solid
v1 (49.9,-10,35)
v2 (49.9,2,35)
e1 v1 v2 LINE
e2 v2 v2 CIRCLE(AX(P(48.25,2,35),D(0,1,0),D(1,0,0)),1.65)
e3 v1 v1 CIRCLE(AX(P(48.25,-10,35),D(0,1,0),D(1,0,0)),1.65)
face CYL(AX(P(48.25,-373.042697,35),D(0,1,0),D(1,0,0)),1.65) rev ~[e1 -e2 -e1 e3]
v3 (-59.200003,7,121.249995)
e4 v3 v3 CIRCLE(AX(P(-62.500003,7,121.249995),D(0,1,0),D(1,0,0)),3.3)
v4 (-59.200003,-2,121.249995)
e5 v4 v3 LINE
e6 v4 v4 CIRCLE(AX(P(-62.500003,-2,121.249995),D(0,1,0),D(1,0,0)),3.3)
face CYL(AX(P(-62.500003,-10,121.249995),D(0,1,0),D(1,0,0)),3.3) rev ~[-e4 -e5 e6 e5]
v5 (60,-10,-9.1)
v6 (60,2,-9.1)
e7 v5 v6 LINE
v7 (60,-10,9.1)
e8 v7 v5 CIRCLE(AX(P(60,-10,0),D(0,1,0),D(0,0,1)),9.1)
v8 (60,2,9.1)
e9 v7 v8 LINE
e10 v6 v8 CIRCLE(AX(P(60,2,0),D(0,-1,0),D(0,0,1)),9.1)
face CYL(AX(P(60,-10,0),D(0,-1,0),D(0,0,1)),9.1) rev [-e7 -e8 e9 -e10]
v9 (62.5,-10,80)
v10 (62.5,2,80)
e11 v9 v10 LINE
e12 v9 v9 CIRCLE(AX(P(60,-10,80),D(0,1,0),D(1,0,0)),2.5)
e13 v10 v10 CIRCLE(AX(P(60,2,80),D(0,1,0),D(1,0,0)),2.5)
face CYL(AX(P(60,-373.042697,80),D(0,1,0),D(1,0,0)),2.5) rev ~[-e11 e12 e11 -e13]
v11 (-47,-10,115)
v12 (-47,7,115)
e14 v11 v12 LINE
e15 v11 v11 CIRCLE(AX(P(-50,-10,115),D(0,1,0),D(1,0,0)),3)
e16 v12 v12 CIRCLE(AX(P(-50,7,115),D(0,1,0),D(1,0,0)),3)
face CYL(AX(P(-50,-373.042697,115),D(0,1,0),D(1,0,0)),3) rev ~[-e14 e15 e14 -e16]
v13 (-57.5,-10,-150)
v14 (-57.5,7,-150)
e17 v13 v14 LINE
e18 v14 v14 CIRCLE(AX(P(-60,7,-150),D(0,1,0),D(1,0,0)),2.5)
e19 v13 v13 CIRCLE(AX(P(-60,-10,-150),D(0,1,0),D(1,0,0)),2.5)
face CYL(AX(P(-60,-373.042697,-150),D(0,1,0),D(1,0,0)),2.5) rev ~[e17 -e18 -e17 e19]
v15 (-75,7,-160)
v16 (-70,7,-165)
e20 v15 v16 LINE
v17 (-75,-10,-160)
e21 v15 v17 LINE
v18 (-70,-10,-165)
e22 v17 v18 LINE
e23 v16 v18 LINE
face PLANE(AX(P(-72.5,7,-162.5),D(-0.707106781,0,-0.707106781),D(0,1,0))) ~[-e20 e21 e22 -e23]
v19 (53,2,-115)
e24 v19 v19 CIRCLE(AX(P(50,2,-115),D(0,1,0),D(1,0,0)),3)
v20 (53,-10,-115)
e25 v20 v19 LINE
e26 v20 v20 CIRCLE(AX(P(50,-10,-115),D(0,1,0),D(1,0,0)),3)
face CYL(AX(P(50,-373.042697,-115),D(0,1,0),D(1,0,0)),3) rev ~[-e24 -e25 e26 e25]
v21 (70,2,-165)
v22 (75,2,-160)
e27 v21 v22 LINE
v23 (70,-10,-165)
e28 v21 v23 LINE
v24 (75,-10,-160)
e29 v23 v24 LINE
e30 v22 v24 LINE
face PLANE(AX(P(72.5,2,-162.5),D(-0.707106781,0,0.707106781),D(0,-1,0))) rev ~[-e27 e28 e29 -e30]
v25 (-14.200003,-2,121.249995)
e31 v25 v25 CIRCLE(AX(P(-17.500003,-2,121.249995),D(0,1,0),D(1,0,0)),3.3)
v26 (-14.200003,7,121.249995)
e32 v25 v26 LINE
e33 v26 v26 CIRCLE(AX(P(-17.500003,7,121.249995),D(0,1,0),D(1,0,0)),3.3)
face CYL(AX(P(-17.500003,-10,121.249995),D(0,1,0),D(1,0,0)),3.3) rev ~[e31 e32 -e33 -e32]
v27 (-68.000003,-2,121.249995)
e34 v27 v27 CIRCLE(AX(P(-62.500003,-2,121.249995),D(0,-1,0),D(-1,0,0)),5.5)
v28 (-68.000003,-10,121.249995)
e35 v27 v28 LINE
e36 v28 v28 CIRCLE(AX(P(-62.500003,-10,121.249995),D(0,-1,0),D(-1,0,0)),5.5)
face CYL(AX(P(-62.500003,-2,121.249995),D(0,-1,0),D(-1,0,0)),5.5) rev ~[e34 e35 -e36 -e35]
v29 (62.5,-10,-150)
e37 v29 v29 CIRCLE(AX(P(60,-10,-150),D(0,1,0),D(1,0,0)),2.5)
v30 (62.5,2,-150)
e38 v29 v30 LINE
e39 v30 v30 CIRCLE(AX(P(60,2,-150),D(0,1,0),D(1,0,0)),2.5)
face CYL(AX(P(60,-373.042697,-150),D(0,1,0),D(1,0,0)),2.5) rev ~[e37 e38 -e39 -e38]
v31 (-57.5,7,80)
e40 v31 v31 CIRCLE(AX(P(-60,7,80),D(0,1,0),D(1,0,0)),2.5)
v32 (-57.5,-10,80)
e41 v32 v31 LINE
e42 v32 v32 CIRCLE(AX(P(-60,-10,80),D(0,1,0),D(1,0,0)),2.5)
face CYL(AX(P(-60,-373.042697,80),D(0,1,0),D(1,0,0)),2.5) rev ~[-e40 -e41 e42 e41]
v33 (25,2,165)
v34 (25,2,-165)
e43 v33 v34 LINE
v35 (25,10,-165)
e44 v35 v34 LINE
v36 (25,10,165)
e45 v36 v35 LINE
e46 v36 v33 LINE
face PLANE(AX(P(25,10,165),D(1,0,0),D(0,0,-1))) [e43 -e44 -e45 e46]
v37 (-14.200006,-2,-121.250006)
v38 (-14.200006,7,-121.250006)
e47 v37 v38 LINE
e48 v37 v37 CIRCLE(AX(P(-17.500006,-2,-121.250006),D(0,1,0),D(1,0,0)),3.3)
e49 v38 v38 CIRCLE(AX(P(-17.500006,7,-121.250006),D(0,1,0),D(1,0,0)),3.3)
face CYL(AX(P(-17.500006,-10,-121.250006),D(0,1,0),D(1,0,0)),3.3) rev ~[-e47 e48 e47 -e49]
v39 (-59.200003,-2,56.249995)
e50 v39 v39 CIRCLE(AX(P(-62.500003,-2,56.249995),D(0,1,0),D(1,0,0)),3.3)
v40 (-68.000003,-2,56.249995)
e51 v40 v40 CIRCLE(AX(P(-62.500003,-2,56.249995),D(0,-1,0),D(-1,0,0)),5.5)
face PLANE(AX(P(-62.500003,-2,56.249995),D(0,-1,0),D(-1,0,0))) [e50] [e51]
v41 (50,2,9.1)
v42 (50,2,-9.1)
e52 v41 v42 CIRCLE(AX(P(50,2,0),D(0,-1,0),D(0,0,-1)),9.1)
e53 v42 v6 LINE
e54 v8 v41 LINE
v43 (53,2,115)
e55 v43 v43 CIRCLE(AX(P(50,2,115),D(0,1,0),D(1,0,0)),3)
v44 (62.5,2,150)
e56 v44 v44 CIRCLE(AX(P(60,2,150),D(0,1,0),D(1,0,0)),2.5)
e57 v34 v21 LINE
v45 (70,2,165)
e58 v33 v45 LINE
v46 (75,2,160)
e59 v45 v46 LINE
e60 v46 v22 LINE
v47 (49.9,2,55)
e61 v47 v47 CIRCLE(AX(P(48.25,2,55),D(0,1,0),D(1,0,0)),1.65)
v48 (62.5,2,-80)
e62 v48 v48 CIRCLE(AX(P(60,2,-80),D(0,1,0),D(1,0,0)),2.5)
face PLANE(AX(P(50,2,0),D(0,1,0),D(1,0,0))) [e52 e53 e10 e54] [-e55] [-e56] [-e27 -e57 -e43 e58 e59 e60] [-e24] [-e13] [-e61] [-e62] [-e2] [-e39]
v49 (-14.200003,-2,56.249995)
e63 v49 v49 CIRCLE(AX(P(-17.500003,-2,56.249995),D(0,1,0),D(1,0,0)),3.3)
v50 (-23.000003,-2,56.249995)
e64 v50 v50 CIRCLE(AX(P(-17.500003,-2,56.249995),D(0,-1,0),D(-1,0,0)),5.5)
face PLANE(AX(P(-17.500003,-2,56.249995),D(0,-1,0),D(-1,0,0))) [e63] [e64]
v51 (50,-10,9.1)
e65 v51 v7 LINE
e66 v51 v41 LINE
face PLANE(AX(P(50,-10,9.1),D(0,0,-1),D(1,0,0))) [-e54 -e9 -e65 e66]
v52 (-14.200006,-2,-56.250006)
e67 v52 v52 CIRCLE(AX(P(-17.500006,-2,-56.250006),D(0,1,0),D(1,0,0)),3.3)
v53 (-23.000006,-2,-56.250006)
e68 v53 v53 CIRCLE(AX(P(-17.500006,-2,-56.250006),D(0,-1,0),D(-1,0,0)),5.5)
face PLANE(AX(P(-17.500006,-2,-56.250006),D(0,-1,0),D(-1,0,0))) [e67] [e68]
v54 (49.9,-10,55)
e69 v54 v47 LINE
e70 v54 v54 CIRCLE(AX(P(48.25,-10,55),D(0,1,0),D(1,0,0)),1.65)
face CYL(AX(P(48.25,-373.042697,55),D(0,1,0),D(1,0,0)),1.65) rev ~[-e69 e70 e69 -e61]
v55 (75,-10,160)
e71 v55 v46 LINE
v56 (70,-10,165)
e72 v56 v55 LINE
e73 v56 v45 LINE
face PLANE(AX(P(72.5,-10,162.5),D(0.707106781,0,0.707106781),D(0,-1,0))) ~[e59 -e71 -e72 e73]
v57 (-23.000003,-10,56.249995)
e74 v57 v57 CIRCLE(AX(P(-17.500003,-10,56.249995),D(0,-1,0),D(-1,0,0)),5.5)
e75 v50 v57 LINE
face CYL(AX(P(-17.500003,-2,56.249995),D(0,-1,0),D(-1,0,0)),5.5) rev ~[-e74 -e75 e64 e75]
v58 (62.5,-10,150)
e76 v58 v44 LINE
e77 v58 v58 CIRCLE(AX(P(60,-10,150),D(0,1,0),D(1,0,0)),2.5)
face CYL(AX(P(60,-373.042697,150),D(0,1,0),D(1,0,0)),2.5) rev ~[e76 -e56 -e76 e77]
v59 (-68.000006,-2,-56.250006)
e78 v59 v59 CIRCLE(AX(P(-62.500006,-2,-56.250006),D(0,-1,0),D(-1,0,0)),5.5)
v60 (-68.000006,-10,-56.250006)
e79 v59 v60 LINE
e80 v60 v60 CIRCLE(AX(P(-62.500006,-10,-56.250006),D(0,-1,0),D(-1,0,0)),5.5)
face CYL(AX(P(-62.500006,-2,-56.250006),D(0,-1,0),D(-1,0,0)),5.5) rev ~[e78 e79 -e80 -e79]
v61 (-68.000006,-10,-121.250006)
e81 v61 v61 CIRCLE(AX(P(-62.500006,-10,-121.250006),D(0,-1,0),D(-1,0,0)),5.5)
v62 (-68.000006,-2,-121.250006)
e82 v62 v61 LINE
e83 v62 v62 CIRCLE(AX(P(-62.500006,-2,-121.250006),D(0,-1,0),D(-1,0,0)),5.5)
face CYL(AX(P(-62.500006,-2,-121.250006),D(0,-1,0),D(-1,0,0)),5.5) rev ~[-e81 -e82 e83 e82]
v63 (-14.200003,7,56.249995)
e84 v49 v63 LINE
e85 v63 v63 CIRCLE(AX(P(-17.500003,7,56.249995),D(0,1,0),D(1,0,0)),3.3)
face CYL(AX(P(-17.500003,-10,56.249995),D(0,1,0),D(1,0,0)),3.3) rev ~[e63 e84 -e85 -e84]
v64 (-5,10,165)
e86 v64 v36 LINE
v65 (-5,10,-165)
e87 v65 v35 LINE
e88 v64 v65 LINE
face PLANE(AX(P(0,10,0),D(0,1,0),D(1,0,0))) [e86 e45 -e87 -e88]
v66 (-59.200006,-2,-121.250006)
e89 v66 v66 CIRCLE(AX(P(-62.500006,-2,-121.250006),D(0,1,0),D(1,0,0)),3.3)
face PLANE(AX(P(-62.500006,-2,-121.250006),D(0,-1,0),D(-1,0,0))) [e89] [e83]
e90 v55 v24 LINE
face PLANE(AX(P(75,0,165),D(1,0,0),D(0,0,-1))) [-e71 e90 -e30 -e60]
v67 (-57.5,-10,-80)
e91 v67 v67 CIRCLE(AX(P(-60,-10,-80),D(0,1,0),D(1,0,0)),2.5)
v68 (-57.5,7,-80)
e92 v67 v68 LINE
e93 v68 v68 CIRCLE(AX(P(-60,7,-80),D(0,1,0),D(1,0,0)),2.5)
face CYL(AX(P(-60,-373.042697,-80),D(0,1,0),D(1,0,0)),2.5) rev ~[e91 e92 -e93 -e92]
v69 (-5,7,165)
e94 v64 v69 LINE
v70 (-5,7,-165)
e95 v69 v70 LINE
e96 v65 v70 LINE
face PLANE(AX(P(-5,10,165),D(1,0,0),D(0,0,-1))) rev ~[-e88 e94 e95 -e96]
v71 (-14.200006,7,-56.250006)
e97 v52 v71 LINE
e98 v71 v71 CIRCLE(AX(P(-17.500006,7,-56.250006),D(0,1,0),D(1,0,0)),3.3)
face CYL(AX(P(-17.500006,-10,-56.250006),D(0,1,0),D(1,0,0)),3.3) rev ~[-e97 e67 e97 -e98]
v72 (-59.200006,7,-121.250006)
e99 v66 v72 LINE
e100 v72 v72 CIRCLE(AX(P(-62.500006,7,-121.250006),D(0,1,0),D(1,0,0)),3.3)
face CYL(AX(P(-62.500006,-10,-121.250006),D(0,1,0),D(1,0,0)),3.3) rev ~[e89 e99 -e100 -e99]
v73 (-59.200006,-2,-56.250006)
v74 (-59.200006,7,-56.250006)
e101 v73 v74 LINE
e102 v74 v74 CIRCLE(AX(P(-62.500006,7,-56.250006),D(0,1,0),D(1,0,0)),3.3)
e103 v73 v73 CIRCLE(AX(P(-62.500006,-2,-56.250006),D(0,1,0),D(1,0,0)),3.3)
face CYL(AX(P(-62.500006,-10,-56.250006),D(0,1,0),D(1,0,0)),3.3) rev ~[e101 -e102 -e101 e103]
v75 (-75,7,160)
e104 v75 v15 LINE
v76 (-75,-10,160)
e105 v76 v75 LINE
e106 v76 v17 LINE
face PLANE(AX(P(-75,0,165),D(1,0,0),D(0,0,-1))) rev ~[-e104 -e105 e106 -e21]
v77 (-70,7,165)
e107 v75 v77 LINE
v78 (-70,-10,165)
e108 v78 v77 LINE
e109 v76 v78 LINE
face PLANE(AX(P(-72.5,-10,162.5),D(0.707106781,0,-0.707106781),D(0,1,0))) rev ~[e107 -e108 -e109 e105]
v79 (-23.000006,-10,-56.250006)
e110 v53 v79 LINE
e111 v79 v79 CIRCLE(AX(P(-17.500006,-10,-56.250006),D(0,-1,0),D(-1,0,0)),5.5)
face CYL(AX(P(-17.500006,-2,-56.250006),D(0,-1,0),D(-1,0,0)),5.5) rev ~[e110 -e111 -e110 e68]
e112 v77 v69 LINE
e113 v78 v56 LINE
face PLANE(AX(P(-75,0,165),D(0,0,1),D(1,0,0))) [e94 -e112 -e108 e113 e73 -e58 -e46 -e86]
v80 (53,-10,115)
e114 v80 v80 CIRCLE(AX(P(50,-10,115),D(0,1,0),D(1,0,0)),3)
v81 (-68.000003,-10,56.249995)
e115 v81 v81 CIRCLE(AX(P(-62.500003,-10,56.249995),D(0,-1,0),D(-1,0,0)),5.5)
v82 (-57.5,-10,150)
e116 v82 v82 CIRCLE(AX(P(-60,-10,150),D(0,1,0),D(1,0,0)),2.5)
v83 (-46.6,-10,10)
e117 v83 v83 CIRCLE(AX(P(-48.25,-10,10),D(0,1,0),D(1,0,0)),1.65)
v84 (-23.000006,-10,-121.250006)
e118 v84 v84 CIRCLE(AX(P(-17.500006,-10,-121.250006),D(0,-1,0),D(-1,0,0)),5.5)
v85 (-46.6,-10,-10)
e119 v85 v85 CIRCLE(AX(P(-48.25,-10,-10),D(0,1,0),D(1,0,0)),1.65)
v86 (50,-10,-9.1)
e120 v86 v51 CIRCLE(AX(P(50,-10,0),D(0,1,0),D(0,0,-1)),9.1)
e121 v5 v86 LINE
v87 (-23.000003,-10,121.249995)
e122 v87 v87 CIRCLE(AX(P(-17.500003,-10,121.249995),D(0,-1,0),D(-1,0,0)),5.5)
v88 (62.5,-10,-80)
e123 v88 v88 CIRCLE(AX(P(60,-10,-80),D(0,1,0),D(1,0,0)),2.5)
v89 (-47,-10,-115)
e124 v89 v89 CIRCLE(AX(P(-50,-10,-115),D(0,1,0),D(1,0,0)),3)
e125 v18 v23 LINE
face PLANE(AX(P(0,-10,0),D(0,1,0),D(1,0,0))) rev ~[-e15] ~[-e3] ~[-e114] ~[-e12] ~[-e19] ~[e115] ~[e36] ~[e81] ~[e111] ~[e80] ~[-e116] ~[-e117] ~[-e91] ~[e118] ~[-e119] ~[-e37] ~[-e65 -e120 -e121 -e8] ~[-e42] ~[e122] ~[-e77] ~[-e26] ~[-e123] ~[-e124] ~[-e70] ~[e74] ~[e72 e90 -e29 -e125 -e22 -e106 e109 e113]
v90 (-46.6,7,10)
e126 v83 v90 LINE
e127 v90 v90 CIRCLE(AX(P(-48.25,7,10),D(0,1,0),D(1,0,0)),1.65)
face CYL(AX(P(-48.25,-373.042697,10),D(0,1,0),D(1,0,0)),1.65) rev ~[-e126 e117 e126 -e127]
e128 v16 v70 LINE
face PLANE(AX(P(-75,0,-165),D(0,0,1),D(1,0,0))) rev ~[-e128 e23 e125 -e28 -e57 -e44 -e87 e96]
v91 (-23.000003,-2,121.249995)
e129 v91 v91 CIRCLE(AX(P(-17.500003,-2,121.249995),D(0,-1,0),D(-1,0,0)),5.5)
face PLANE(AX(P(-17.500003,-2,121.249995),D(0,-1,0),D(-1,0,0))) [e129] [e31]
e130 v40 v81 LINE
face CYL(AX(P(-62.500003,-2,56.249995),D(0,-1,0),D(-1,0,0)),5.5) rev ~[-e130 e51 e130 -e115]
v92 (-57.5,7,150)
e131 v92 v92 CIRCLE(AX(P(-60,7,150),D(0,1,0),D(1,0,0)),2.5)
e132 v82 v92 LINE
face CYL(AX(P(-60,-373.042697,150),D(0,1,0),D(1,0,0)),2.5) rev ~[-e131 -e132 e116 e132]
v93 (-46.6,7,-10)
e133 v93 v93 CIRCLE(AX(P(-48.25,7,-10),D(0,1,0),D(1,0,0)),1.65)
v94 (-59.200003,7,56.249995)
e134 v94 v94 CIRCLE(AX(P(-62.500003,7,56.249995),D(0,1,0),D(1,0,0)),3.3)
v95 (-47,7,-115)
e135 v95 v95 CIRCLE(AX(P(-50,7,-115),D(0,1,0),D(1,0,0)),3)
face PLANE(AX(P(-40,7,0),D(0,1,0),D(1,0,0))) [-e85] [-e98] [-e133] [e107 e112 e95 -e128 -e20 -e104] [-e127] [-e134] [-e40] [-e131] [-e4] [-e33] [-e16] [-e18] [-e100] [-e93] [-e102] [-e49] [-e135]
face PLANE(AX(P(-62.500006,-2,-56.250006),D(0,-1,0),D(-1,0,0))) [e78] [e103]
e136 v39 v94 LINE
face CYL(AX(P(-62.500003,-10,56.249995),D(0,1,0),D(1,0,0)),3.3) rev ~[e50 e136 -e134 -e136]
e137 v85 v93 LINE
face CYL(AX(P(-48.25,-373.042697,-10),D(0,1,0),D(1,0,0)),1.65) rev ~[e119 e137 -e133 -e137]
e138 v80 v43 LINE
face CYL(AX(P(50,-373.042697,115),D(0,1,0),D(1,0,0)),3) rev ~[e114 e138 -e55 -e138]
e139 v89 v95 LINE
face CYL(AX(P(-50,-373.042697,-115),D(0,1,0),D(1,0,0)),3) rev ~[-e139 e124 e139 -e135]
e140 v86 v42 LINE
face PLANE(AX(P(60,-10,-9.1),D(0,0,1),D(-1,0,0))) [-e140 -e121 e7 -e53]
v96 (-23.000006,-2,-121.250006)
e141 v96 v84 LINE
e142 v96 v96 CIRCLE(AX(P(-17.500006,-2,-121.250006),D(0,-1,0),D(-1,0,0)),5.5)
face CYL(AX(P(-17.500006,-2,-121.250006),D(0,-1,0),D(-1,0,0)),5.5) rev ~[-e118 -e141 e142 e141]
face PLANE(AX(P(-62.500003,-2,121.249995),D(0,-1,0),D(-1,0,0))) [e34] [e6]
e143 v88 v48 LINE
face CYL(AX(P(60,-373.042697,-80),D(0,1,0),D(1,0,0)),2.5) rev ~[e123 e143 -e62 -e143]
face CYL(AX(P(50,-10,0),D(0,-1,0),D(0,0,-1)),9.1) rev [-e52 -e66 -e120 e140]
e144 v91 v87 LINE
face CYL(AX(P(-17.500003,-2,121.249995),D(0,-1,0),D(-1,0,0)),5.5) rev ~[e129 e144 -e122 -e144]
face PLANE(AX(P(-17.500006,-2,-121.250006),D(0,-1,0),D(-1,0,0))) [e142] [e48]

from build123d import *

# Parameters (mm, degrees)
SKETCH_1_W                   = 150
SKETCH_1_H                   = 330
EXTRUDE_1_DEPTH              = 10
SKETCH_2_W                   = 70
SKETCH_2_H                   = 330
CUT_EXTRUDE_1_DEPTH          = 3
SKETCH_3_W                   = 50
SKETCH_3_H                   = 330
CUT_EXTRUDE_2_DEPTH          = 8
MM_1_D                       = 1
HOLE_WIZARD_M6_1_D           = 6.6
HOLE_WIZARD_M6_1_CBORE_D     = 11
HOLE_WIZARD_M6_1_CBORE_DEPTH = 8
MM_0_D                       = 6
HOLE_WIZARD_M6_1_2_D         = 5
CHAMFER_1_SIZE               = 5
CUT_EXTRUDE_3_DEPTH          = 183.345825288
HOLE_WIZARD_M4_1_D           = 3.3


with BuildPart() as part:
    # 草图1 → 凸台-拉伸1 (new, symmetric)
    with BuildSketch(Plane(origin=(0, 0, 0), x_dir=(1, 0, 0), z_dir=(0, 1, 0))):
        Rectangle(SKETCH_1_W, SKETCH_1_H)
    extrude(amount=EXTRUDE_1_DEPTH, both=True)

    # 草图2 → 切除-拉伸1 (cut)
    with BuildSketch(Plane(origin=(0, 10, 0), x_dir=(1, 0, 0), z_dir=(0, 1, 0))):
        with Locations((-40, 0)):
            Rectangle(SKETCH_2_W, SKETCH_2_H)
    extrude(amount=-CUT_EXTRUDE_1_DEPTH, mode=Mode.SUBTRACT)

    # 草图3 → 切除-拉伸2 (cut)
    with BuildSketch(Plane(origin=(0, 10, 0), x_dir=(1, 0, 0), z_dir=(0, 1, 0))):
        with Locations((50, 0)):
            Rectangle(SKETCH_3_W, SKETCH_3_H)
    extrude(amount=-CUT_EXTRUDE_2_DEPTH, mode=Mode.SUBTRACT)

    # 大小mm 暗销孔1 (through all)
    with Locations(Plane(origin=(0, 7, 0), x_dir=(1, 0, 0), z_dir=(0, 1, 0))):
        with Locations((-62.500006208, 121.250006208), (-17.500006208, 121.250006208), (-62.500006208, 56.250006208), (-17.500006208, 56.250006208), (-62.500003219, -56.249995139), (-17.500003219, -56.249995139), (-62.500003219, -121.249995139), (-17.500003219, -121.249995139)):
            Hole(MM_1_D / 2)

    # Hole Wizard M6 _1 (through all)
    with Locations(Plane(origin=(0, -10, 0), x_dir=(-1, 0, 0), z_dir=(0, -1, 0))):
        with Locations((17.500006208, 121.250006208), (62.500006208, 121.250006208), (17.500006208, 56.250006208), (62.500006208, 56.250006208), (17.500003219, -56.249995139), (62.500003219, -56.249995139), (17.500003219, -121.249995139), (62.500003219, -121.249995139)):
            CounterBoreHole(HOLE_WIZARD_M6_1_D / 2, HOLE_WIZARD_M6_1_CBORE_D / 2, HOLE_WIZARD_M6_1_CBORE_DEPTH)

    # 大小mm 暗销孔0 (through all)
    with Locations(Plane(origin=(0, -10, 0), x_dir=(-1, 0, 0), z_dir=(0, -1, 0))):
        with Locations((-50.000000134, 114.999999999), (-50.000000032, -114.999999953), (49.999999866, 114.999999999), (49.999999968, -114.999999953)):
            Hole(MM_0_D / 2)

    # Hole Wizard M6 _1 2 (through all)
    with Locations(Plane(origin=(0, -10, 0), x_dir=(-1, 0, 0), z_dir=(0, -1, 0))):
        with Locations((59.999999968, -149.999999953), (-60.000000032, -149.999999953), (-60.000000032, -79.999999953), (59.999999968, -79.999999953), (59.999999866, 79.999999999), (59.999999866, 149.999999999), (-60.000000134, 149.999999999), (-60.000000134, 79.999999999)):
            Hole(HOLE_WIZARD_M6_1_2_D / 2)

    # 倒角1
    chamfer_1_edges = [part.edges().sort_by_distance(p)[0] for p in [
        (-75, -1.5, -165),
        (-75, -1.5, 165),
        (75, -4, -165),
        (75, -4, 165),
    ]]
    chamfer(chamfer_1_edges, length=CHAMFER_1_SIZE)

    # 草图14 → 切除-拉伸3 (cut, through all)
    with BuildSketch(Plane.XZ.offset(10)):
        with BuildLine():
            Line((50, 9.1), (60, 9.1))
            ThreePointArc((60, 9.1), (69.1, 0), (60, -9.1))
            Line((60, -9.1), (50, -9.1))
            ThreePointArc((50, -9.1), (40.9, 0), (50, 9.1))
        make_face()
    extrude(amount=-CUT_EXTRUDE_3_DEPTH, mode=Mode.SUBTRACT)

    # M4 螺纹孔1 (through all)
    with Locations(Plane(origin=(0, -10, 0), x_dir=(-1, 0, 0), z_dir=(0, -1, 0))):
        with Locations((-48.25000003, -35.000000224), (-48.25000003, -55.000000224), (48.249999938, -10.000000156), (48.249999938, 9.999999844)):
            Hole(HOLE_WIZARD_M4_1_D / 2)


solid = part.part
